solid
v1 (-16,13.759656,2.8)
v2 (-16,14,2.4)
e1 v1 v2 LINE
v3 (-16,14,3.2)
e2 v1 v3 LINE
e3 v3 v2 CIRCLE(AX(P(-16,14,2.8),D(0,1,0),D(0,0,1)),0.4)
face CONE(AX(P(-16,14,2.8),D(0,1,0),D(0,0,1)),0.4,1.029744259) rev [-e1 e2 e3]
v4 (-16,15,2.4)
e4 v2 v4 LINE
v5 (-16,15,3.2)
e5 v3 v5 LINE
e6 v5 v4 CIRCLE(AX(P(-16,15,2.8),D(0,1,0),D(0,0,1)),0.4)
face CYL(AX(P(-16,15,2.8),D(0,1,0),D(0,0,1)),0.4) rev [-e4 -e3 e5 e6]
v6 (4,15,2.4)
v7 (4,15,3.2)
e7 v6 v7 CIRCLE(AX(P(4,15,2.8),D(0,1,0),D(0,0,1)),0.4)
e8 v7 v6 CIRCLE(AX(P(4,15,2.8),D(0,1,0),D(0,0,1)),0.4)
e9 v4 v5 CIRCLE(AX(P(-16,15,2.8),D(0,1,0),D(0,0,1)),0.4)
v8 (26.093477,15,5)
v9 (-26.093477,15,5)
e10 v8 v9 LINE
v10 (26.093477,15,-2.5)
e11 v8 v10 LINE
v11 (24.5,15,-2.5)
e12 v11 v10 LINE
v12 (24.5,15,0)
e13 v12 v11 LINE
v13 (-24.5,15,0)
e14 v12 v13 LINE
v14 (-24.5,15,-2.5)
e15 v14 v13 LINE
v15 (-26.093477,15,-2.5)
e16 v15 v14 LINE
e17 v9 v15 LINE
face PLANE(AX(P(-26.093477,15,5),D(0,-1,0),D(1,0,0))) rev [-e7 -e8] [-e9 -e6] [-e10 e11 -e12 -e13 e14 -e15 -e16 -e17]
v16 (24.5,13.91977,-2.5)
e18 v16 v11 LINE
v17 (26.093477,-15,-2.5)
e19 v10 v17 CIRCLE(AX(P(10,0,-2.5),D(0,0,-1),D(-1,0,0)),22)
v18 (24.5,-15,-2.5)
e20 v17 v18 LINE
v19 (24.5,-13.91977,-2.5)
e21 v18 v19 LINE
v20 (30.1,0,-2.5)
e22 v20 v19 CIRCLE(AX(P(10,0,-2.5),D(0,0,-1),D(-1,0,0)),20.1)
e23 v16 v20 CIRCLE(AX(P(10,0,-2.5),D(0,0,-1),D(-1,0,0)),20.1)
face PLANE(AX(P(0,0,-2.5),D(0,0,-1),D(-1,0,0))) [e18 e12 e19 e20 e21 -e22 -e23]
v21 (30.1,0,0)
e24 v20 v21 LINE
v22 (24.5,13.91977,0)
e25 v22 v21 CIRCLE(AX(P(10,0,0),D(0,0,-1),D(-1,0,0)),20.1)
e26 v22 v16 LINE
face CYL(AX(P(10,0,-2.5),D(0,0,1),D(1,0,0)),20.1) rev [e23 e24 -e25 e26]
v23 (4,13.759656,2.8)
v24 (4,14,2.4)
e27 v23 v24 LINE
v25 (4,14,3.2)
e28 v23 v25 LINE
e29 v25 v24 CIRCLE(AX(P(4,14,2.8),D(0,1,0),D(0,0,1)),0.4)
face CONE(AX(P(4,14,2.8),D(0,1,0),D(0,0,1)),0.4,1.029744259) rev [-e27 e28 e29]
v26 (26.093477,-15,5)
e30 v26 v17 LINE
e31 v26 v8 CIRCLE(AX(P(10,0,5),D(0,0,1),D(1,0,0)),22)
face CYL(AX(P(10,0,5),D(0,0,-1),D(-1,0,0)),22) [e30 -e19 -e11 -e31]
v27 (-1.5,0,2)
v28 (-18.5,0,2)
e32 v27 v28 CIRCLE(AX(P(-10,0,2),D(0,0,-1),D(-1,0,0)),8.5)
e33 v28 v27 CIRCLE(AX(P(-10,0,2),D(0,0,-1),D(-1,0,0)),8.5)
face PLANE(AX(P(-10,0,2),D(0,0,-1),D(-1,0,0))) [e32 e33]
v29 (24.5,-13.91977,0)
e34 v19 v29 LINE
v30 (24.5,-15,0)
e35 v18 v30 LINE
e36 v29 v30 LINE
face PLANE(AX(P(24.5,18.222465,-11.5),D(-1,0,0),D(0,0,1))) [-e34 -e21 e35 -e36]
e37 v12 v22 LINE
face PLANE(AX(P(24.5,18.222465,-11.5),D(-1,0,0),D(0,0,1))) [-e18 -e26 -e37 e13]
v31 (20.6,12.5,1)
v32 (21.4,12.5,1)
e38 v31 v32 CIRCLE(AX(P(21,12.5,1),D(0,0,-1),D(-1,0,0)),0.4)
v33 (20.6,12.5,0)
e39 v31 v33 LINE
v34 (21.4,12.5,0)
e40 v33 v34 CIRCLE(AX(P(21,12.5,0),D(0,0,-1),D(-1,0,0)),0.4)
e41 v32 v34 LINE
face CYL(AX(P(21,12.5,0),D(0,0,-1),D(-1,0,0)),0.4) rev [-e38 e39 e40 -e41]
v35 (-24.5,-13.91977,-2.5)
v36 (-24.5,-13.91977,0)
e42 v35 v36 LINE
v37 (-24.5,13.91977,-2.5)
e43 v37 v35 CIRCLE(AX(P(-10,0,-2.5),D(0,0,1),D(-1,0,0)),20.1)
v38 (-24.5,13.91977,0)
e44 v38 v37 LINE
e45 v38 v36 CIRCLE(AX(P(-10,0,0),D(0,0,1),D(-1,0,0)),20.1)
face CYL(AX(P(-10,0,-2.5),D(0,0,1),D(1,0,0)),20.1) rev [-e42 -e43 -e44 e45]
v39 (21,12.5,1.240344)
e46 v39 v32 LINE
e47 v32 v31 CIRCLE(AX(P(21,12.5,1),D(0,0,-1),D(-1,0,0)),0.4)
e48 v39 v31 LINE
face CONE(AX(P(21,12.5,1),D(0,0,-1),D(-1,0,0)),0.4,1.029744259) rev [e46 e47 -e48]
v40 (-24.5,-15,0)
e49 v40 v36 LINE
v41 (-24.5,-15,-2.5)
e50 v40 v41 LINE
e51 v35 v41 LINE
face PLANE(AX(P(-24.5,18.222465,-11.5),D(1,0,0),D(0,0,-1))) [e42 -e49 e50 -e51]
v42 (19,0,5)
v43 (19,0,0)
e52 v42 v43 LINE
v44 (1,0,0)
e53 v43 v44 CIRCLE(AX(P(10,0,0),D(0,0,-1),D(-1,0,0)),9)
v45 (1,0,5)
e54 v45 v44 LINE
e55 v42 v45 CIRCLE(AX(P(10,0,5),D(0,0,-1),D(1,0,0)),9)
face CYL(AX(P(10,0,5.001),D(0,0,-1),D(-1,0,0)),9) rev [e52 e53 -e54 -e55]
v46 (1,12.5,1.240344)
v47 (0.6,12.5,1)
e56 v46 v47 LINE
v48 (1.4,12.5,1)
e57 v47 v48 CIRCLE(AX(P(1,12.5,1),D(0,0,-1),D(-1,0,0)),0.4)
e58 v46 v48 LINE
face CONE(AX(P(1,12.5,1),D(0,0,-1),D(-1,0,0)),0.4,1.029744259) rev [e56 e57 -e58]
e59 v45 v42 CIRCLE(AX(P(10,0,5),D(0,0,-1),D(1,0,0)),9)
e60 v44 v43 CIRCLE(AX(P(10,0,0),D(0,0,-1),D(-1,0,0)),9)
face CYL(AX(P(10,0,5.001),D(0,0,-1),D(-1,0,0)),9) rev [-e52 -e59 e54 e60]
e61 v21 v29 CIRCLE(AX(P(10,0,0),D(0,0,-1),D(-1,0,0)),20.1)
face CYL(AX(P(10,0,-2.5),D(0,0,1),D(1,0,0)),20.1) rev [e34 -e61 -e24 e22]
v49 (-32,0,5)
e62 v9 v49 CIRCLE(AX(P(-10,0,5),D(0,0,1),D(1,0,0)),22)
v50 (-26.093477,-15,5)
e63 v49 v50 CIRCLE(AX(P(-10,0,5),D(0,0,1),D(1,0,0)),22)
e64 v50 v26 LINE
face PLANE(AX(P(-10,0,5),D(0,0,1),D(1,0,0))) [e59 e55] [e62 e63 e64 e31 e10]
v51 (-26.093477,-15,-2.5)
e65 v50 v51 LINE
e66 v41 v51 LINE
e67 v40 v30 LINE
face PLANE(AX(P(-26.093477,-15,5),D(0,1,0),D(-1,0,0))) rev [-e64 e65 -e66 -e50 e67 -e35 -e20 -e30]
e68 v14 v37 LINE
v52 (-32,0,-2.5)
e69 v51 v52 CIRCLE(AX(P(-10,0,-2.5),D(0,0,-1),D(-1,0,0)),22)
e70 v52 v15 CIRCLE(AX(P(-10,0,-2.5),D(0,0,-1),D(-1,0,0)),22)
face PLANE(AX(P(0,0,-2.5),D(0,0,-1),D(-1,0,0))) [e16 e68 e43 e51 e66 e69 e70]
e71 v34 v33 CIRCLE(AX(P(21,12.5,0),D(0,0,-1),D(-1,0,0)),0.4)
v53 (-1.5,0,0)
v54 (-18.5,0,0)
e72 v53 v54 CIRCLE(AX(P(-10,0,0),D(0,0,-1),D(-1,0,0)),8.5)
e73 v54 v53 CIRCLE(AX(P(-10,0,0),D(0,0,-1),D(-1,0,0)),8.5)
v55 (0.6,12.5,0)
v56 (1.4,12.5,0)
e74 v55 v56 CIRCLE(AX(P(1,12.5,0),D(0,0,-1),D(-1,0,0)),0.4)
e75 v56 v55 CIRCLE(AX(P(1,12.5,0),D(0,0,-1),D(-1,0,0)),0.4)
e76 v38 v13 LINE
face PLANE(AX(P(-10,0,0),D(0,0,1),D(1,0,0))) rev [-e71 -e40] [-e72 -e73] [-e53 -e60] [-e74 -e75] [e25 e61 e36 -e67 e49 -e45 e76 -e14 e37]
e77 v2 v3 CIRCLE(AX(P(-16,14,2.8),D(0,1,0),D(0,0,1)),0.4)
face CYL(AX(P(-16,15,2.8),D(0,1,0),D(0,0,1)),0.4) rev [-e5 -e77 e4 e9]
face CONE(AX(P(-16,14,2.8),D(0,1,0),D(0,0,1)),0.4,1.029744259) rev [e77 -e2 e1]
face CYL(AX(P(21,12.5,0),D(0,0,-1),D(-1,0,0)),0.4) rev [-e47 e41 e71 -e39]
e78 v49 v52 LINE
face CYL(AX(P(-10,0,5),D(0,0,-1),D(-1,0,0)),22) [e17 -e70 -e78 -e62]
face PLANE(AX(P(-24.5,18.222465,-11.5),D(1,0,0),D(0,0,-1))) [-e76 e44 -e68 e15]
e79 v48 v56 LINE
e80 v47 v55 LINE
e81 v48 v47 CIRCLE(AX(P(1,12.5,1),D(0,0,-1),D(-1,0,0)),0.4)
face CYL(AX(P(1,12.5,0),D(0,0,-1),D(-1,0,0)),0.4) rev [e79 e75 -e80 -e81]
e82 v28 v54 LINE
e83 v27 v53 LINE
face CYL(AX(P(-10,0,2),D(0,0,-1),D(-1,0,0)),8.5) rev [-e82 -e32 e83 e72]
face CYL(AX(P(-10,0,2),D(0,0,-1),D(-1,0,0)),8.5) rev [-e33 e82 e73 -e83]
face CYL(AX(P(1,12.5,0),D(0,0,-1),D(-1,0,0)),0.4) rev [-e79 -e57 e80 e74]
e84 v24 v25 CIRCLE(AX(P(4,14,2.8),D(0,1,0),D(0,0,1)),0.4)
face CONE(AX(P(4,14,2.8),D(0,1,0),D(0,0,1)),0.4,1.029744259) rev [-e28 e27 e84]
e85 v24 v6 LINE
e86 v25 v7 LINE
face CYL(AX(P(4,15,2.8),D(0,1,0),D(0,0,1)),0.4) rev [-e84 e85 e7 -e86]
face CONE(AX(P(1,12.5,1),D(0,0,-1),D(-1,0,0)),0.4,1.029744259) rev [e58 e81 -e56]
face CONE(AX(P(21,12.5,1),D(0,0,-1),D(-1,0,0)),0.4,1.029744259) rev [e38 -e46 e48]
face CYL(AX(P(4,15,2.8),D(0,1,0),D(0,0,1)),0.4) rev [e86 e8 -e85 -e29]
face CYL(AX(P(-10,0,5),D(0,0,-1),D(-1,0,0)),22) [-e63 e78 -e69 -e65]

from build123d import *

# Parameters (mm, degrees)
SKETCH1_R                      = 2
BOSS_EXTRUDE1_DEPTH            = 5
SKETCH2_R                      = 8.5
CUT_EXTRUDE1_DEPTH             = 2
CUT_EXTRUDE2_REACH             = 37.693
SKETCH3_R                      = 9
BOSS_EXTRUDE2_START            = 2.5
BOSS_EXTRUDE2_DEPTH            = 2.5
SKETCH5_W                      = 49
SKETCH5_H                      = 36.444930448
CUT_EXTRUDE3_DEPTH             = 11.5
F_0_8_0_8_DIAMETER_HOLE1_D     = 0.8
F_0_8_0_8_DIAMETER_HOLE1_DEPTH = 1
F_0_8_0_8_DIAMETER_HOLE1_TIP   = 0.240344248
SKETCH8_R                      = 2
BOSS_EXTRUDE3_DEPTH            = 3
F_0_8_0_8_DIAMETER_HOLE2_D     = 0.8
F_0_8_0_8_DIAMETER_HOLE2_DEPTH = 1
F_0_8_0_8_DIAMETER_HOLE2_TIP   = 0.240344248


with BuildPart() as part:
    # Sketch1 → Boss-Extrude1 (new body)
    with BuildSketch(Plane.XY):
        with BuildLine():
            Line((-26.093476939, 15), (26.093476939, 15))
            ThreePointArc((26.093476939, 15), (32, 0), (26.093476939, -15))
            Line((26.093476939, -15), (-26.093476939, -15))
            ThreePointArc((-26.093476939, -15), (-32, 0), (-26.093476939, 15))
        make_face()
        with Locations((-10, 0)):
            Circle(SKETCH1_R, mode=Mode.SUBTRACT)
        with Locations((10, 0)):
            Circle(SKETCH1_R, mode=Mode.SUBTRACT)
    extrude(amount=BOSS_EXTRUDE1_DEPTH)

    # Sketch2 → Cut-Extrude1 (cut)
    with BuildSketch(Plane(origin=(0, 0, 0), x_dir=(-1, 0, 0), z_dir=(0, 0, -1))):
        with Locations((10, 0)):
            Circle(SKETCH2_R)
    extrude(amount=-CUT_EXTRUDE1_DEPTH, mode=Mode.SUBTRACT)

    # Sketch3 → Cut-Extrude2 (cut, up to next)
    with BuildSketch(Plane(origin=(0, 0, 0), x_dir=(-1, 0, 0), z_dir=(0, 0, -1)), mode=Mode.PRIVATE) as cut_extrude2_sk1:
        with Locations((-10, 0)):
            Circle(SKETCH3_R)
    cut_extrude2_tool1 = extrude(cut_extrude2_sk1.sketch, amount=-CUT_EXTRUDE2_REACH, mode=Mode.PRIVATE) & part.part
    add(cut_extrude2_tool1.solids().sort_by_distance((10, 0, 0))[0], mode=Mode.SUBTRACT)

    # Sketch4 → Boss-Extrude2 (add)
    with BuildSketch(Plane(origin=(0, 0, 0), x_dir=(-1, 0, 0), z_dir=(0, 0, -1)).offset(BOSS_EXTRUDE2_START)):
        with BuildLine():
            ThreePointArc((26.093476939, -15), (32, 0), (26.093476939, 15))
            Line((26.093476939, 15), (23.379461873, 15))
            ThreePointArc((23.379461873, 15), (30.1, 0), (23.379461873, -15))
            Line((23.379461873, -15), (26.093476939, -15))
        make_face()
        with BuildLine():
            ThreePointArc((-26.093476939, 15), (-32, 0), (-26.093476939, -15))
            Line((-26.093476939, -15), (-23.379461873, -15))
            ThreePointArc((-23.379461873, -15), (-30.1, 0), (-23.379461873, 15))
            Line((-23.379461873, 15), (-26.093476939, 15))
        make_face()
    extrude(amount=-BOSS_EXTRUDE2_DEPTH)

    # Sketch5 → Cut-Extrude3 (cut)
    with BuildSketch(Plane(origin=(0, 0, 0), x_dir=(-1, 0, 0), z_dir=(0, 0, -1))):
        Rectangle(SKETCH5_W, SKETCH5_H)
    extrude(amount=CUT_EXTRUDE3_DEPTH, mode=Mode.SUBTRACT)

    # Ø0.8 (0.8) Diameter Hole1
    with Locations(Plane(origin=(1, 12.5, 0), x_dir=(-1, 0, 0), z_dir=(0, 0, -1))):
        with Locations((0, 0), (-20, 0)):
            Hole(F_0_8_0_8_DIAMETER_HOLE1_D / 2, depth=F_0_8_0_8_DIAMETER_HOLE1_DEPTH)
            with Locations((0, 0, -(F_0_8_0_8_DIAMETER_HOLE1_DEPTH + F_0_8_0_8_DIAMETER_HOLE1_TIP / 2))):  # 118° drill point
                Cone(0, F_0_8_0_8_DIAMETER_HOLE1_D / 2, F_0_8_0_8_DIAMETER_HOLE1_TIP, mode=Mode.SUBTRACT)

    # Sketch8 → Boss-Extrude3 (add)
    with BuildSketch(Plane(origin=(0, 0, 2), x_dir=(-1, 0, 0), z_dir=(0, 0, -1))):
        with Locations((10, 0)):
            Circle(SKETCH8_R)
    extrude(amount=-BOSS_EXTRUDE3_DEPTH)

    # Ø0.8 (0.8) Diameter Hole2
    with Locations(Plane(origin=(-16, 15, 2.8), x_dir=(1, 0, 0), z_dir=(0, 1, 0))):
        with Locations((0, 0), (20, 0)):
            Hole(F_0_8_0_8_DIAMETER_HOLE2_D / 2, depth=F_0_8_0_8_DIAMETER_HOLE2_DEPTH)
            with Locations((0, 0, -(F_0_8_0_8_DIAMETER_HOLE2_DEPTH + F_0_8_0_8_DIAMETER_HOLE2_TIP / 2))):  # 118° drill point
                Cone(0, F_0_8_0_8_DIAMETER_HOLE2_D / 2, F_0_8_0_8_DIAMETER_HOLE2_TIP, mode=Mode.SUBTRACT)


solid = part.part
